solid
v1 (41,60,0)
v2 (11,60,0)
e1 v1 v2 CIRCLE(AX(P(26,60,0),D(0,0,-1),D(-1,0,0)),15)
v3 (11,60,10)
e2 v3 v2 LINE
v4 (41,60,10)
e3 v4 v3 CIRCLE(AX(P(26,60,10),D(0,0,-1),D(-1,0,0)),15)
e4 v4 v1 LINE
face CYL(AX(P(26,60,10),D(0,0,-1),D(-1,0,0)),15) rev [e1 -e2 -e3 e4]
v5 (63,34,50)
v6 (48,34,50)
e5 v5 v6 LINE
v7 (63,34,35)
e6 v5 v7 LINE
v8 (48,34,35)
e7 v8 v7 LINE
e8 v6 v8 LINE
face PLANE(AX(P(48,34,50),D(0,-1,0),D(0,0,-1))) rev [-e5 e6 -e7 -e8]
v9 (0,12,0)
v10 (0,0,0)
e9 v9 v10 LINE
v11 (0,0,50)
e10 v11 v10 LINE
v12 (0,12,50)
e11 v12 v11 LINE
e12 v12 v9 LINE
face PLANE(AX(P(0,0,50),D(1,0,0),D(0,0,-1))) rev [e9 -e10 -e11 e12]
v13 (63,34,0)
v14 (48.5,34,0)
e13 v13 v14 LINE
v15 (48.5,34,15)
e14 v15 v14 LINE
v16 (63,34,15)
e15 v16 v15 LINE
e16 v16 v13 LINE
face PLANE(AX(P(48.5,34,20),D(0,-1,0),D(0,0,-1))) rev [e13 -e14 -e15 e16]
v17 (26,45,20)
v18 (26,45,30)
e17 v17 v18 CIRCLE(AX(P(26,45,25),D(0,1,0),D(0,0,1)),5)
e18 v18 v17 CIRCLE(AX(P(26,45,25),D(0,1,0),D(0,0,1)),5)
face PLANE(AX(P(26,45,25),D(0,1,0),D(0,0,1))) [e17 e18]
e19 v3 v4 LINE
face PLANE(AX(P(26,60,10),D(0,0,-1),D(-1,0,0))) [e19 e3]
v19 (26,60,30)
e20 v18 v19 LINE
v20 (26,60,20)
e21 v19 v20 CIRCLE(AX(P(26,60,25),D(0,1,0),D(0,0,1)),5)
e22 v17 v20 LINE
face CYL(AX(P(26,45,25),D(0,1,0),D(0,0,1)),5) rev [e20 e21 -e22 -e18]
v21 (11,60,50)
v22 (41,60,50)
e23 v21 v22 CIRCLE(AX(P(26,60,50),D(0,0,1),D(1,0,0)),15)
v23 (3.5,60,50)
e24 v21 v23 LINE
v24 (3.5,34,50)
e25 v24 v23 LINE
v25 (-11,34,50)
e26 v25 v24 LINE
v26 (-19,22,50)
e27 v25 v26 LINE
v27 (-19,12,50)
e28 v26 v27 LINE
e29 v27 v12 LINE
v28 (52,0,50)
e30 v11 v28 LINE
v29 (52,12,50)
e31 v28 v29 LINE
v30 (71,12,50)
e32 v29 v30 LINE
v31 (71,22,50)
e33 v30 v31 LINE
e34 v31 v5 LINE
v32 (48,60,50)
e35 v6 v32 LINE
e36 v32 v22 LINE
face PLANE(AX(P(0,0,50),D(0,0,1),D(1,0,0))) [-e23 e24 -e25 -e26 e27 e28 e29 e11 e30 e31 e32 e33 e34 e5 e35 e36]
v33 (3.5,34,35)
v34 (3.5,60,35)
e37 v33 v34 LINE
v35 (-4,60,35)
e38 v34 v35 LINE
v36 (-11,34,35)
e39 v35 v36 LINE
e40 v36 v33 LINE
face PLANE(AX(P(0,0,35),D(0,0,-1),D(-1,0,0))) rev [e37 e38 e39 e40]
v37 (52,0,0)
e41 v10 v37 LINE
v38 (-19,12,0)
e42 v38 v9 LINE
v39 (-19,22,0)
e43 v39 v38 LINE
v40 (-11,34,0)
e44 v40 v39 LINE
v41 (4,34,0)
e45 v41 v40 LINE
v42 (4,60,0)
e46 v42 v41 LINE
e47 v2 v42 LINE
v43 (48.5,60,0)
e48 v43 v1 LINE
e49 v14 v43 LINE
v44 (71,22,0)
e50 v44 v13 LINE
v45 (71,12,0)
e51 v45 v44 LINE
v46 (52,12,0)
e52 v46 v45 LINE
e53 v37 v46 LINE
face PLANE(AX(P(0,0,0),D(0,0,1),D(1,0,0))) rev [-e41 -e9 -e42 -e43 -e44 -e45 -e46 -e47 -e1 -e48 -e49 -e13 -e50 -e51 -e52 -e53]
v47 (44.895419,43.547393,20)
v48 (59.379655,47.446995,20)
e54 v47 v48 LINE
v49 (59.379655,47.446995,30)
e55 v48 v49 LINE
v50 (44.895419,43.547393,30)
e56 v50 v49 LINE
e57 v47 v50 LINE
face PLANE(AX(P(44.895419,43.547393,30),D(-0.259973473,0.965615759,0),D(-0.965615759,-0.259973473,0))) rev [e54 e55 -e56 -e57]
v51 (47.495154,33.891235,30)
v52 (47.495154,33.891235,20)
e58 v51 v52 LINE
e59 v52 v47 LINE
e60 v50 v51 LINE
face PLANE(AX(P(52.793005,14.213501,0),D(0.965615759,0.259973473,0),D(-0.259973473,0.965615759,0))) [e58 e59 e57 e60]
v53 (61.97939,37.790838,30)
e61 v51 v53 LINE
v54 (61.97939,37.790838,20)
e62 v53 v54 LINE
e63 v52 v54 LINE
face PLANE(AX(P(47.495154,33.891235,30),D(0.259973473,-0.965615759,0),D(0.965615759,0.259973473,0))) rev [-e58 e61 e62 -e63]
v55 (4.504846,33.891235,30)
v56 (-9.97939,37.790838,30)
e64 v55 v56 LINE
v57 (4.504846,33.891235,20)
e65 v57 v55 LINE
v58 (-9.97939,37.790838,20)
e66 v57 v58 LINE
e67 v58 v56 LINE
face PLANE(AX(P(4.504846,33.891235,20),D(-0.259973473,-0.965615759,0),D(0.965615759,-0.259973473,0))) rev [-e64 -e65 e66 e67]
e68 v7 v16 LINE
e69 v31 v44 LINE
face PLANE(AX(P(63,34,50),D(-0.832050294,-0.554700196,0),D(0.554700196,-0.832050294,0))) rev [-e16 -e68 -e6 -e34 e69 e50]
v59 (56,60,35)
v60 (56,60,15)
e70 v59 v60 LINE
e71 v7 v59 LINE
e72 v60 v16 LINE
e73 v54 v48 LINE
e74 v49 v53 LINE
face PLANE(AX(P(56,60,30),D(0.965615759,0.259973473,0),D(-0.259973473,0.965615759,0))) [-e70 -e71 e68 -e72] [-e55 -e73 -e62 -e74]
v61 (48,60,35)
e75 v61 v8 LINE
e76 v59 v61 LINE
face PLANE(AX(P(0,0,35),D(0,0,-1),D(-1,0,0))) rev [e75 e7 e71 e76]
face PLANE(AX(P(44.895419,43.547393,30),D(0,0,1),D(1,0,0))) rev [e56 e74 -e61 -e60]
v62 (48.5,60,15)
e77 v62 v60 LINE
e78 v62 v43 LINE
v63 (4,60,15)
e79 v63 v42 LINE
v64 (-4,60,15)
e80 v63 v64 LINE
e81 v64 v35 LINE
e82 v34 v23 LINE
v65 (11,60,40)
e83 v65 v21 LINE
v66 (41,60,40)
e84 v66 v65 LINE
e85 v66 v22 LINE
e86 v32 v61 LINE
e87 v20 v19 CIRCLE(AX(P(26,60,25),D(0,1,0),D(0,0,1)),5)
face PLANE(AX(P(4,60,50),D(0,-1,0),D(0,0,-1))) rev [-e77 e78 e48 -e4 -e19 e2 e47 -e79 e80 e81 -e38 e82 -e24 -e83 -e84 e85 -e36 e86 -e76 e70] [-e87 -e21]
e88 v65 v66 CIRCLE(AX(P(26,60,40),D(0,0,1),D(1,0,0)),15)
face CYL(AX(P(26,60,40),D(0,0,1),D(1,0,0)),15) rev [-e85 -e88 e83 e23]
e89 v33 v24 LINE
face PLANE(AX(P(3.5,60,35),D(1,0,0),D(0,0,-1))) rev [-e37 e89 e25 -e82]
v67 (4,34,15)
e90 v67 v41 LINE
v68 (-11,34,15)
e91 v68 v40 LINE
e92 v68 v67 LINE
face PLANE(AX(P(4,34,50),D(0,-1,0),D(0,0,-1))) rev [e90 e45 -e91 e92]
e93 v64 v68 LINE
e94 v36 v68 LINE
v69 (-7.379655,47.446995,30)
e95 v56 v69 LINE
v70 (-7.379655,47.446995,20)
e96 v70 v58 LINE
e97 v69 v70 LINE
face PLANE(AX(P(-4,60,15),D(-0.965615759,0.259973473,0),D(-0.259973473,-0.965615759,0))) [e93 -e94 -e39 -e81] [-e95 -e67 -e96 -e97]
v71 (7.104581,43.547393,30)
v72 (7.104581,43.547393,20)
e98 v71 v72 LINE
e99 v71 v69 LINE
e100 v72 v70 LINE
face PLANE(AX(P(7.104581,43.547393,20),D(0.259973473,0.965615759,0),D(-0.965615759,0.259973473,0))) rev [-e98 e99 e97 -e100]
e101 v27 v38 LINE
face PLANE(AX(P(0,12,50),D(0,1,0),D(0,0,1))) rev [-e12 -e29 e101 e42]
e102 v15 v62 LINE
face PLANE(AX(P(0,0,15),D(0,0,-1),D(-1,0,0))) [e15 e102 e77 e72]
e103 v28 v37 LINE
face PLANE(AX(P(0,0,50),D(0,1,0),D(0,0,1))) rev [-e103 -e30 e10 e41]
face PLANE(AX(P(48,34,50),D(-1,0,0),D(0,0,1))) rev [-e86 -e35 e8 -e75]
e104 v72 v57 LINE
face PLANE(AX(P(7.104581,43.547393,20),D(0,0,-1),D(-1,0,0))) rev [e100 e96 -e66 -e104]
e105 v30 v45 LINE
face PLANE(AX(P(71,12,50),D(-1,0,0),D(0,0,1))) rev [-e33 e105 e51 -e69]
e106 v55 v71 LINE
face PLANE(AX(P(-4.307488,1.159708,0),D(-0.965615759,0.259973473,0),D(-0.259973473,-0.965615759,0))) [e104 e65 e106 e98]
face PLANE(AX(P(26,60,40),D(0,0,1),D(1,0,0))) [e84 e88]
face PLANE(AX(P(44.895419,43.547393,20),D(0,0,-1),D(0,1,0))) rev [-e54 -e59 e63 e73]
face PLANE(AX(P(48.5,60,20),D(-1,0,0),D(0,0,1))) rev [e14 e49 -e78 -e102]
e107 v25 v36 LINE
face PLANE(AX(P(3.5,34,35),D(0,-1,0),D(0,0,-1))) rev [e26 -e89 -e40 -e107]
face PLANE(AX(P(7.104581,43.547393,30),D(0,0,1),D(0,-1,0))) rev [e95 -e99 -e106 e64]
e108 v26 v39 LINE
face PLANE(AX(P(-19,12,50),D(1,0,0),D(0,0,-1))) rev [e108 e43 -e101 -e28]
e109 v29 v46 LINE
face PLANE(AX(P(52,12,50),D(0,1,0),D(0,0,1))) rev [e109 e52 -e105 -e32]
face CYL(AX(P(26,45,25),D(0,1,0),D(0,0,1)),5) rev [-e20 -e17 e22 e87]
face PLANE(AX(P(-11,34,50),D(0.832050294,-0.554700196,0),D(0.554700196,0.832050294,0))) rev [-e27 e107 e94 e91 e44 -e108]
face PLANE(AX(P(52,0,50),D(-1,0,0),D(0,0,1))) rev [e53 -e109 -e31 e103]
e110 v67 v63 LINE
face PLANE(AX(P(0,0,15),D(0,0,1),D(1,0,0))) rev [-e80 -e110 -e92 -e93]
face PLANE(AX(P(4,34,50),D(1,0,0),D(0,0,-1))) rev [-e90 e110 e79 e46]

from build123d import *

# Parameters (mm, degrees)
BASE_BLOCK_DEPTH        = 50
SADDLE_CUT_1_30_DEPTH   = 10
SADDLE_START            = -10
SADDLE_CUT_2_30_DEPTH   = 10
UPPER_BLOCK_DEPTH       = 30
UPPER_BLOCK_NOTCH_DEPTH = 20
NOTCH_PAD_1_DEPTH       = 5
NOTCH_PAD_2_DEPTH       = 5
SIDE_BLOCK_DEPTH        = 35
SIDE_BLOCK_POCKET_DEPTH = 15
TOP_HOLE_SKETCH_R       = 5
TOP_HOLE_10_DEPTH       = 15
SIDE_WINDOW_SKETCH_W    = 10
SIDE_WINDOW_SKETCH_H    = 10
SIDE_WINDOW_CUT_DEPTH   = 15
UPPER_WINDOW_SKETCH_W   = 10
UPPER_WINDOW_SKETCH_H   = 10
UPPER_WINDOW_CUT_DEPTH  = 15


with BuildPart() as part:
    # Base Profile Sketch → Base Block (new body)
    with BuildSketch(Plane.XY):
        Polygon((0, 0), (52, 0), (52, 12), (71, 12), (71, 22), (63, 34), (48, 34), (48, 60), (4, 60), (4, 34), (-11, 34), (-19, 22), (-19, 12), (0, 12), align=None)
    extrude(amount=BASE_BLOCK_DEPTH)

    # Saddle Cut 1 Sketch → Saddle Cut 1 Ø30 (cut)
    with BuildSketch(Plane.XY.offset(50)):
        with BuildLine():
            Line((11, 60), (41, 60))
            ThreePointArc((41, 60), (26, 45), (11, 60))
        make_face()
    extrude(amount=-SADDLE_CUT_1_30_DEPTH, mode=Mode.SUBTRACT)

    # Saddle Cut 2 Sketch → Saddle Cut 2 Ø30 (cut)
    with BuildSketch(Plane(origin=(0, 0, 0), x_dir=(-1, 0, 0), z_dir=(0, 0, -1)).offset(SADDLE_START)):
        with BuildLine():
            Line((-41, 60), (-11, 60))
            ThreePointArc((-11, 60), (-26, 45), (-41, 60))
        make_face()
    extrude(amount=SADDLE_CUT_2_30_DEPTH, mode=Mode.SUBTRACT)

    # Upper Block Sketch → Upper Block (add)
    with BuildSketch(Plane(origin=(0, 0, 0), x_dir=(-1, 0, 0), z_dir=(0, 0, -1))):
        Polygon((-48, 60), (-48, 34), (-63, 34), (-56, 60), align=None)
    extrude(amount=-UPPER_BLOCK_DEPTH)

    # Upper Block Notch Sketch → Upper Block Notch (cut)
    with BuildSketch(Plane(origin=(0, 0, 0), x_dir=(-1, 0, 0), z_dir=(0, 0, -1))):
        Polygon((-63, 34), (-56, 60), (-48.5, 60), (-48.5, 34), align=None)
    extrude(amount=-UPPER_BLOCK_NOTCH_DEPTH, mode=Mode.SUBTRACT)

    # Notch Pad 1 Sketch → Notch Pad 1 (add)
    with BuildSketch(Plane(origin=(0, 0, 20), x_dir=(-1, 0, 0), z_dir=(0, 0, -1))):
        Polygon((-63, 34), (-48.5, 34), (-48.5, 60), (-56, 60), align=None)
    extrude(amount=NOTCH_PAD_1_DEPTH)

    # Notch Pad 2 Sketch → Notch Pad 2 (add)
    with BuildSketch(Plane.XY.offset(30)):
        Polygon((48, 60), (56, 60), (63, 34), (48, 34), align=None)
    extrude(amount=NOTCH_PAD_2_DEPTH)

    # Side Block Sketch → Side Block (add)
    with BuildSketch(Plane.XY.offset(50)):
        Polygon((4, 60), (4, 34), (-11, 34), (-4, 60), align=None)
    extrude(amount=-SIDE_BLOCK_DEPTH)

    # Side Block Pocket Sketch → Side Block Pocket (cut)
    with BuildSketch(Plane.XY.offset(50)):
        Polygon((3.5, 60), (3.5, 34), (-11, 34), (-4, 60), align=None)
    extrude(amount=-SIDE_BLOCK_POCKET_DEPTH, mode=Mode.SUBTRACT)

    # Top Hole Sketch → Top Hole Ø10 (cut)
    with BuildSketch(Plane(origin=(0, 60, 0), x_dir=(1, 0, 0), z_dir=(0, 1, 0))):
        with Locations(Location((26, -25, 0), (0, 0, 270))):
            Circle(TOP_HOLE_SKETCH_R)
    extrude(amount=-TOP_HOLE_10_DEPTH, mode=Mode.SUBTRACT)

    # Side Window Sketch → Side Window Cut (cut)
    with BuildSketch(Plane(origin=(-18.791724138, 5.059310345, 0), x_dir=(0, 0, 1), z_dir=(-0.9656157585206698, 0.25997347344787275, 0))):
        with Locations((25, 38.897051617)):
            Rectangle(SIDE_WINDOW_SKETCH_W, SIDE_WINDOW_SKETCH_H)
    extrude(amount=-SIDE_WINDOW_CUT_DEPTH, mode=Mode.SUBTRACT)

    # Upper Window Sketch → Upper Window Cut (cut)
    with BuildSketch(Plane(origin=(67.277241379, 18.113103448, 0), x_dir=(0, 0, -1), z_dir=(0.9656157585206697, 0.2599734734478728, 0))):
        with Locations((-25, 25.378430998)):
            Rectangle(UPPER_WINDOW_SKETCH_W, UPPER_WINDOW_SKETCH_H)
    extrude(amount=-UPPER_WINDOW_CUT_DEPTH, mode=Mode.SUBTRACT)


solid = part.part
